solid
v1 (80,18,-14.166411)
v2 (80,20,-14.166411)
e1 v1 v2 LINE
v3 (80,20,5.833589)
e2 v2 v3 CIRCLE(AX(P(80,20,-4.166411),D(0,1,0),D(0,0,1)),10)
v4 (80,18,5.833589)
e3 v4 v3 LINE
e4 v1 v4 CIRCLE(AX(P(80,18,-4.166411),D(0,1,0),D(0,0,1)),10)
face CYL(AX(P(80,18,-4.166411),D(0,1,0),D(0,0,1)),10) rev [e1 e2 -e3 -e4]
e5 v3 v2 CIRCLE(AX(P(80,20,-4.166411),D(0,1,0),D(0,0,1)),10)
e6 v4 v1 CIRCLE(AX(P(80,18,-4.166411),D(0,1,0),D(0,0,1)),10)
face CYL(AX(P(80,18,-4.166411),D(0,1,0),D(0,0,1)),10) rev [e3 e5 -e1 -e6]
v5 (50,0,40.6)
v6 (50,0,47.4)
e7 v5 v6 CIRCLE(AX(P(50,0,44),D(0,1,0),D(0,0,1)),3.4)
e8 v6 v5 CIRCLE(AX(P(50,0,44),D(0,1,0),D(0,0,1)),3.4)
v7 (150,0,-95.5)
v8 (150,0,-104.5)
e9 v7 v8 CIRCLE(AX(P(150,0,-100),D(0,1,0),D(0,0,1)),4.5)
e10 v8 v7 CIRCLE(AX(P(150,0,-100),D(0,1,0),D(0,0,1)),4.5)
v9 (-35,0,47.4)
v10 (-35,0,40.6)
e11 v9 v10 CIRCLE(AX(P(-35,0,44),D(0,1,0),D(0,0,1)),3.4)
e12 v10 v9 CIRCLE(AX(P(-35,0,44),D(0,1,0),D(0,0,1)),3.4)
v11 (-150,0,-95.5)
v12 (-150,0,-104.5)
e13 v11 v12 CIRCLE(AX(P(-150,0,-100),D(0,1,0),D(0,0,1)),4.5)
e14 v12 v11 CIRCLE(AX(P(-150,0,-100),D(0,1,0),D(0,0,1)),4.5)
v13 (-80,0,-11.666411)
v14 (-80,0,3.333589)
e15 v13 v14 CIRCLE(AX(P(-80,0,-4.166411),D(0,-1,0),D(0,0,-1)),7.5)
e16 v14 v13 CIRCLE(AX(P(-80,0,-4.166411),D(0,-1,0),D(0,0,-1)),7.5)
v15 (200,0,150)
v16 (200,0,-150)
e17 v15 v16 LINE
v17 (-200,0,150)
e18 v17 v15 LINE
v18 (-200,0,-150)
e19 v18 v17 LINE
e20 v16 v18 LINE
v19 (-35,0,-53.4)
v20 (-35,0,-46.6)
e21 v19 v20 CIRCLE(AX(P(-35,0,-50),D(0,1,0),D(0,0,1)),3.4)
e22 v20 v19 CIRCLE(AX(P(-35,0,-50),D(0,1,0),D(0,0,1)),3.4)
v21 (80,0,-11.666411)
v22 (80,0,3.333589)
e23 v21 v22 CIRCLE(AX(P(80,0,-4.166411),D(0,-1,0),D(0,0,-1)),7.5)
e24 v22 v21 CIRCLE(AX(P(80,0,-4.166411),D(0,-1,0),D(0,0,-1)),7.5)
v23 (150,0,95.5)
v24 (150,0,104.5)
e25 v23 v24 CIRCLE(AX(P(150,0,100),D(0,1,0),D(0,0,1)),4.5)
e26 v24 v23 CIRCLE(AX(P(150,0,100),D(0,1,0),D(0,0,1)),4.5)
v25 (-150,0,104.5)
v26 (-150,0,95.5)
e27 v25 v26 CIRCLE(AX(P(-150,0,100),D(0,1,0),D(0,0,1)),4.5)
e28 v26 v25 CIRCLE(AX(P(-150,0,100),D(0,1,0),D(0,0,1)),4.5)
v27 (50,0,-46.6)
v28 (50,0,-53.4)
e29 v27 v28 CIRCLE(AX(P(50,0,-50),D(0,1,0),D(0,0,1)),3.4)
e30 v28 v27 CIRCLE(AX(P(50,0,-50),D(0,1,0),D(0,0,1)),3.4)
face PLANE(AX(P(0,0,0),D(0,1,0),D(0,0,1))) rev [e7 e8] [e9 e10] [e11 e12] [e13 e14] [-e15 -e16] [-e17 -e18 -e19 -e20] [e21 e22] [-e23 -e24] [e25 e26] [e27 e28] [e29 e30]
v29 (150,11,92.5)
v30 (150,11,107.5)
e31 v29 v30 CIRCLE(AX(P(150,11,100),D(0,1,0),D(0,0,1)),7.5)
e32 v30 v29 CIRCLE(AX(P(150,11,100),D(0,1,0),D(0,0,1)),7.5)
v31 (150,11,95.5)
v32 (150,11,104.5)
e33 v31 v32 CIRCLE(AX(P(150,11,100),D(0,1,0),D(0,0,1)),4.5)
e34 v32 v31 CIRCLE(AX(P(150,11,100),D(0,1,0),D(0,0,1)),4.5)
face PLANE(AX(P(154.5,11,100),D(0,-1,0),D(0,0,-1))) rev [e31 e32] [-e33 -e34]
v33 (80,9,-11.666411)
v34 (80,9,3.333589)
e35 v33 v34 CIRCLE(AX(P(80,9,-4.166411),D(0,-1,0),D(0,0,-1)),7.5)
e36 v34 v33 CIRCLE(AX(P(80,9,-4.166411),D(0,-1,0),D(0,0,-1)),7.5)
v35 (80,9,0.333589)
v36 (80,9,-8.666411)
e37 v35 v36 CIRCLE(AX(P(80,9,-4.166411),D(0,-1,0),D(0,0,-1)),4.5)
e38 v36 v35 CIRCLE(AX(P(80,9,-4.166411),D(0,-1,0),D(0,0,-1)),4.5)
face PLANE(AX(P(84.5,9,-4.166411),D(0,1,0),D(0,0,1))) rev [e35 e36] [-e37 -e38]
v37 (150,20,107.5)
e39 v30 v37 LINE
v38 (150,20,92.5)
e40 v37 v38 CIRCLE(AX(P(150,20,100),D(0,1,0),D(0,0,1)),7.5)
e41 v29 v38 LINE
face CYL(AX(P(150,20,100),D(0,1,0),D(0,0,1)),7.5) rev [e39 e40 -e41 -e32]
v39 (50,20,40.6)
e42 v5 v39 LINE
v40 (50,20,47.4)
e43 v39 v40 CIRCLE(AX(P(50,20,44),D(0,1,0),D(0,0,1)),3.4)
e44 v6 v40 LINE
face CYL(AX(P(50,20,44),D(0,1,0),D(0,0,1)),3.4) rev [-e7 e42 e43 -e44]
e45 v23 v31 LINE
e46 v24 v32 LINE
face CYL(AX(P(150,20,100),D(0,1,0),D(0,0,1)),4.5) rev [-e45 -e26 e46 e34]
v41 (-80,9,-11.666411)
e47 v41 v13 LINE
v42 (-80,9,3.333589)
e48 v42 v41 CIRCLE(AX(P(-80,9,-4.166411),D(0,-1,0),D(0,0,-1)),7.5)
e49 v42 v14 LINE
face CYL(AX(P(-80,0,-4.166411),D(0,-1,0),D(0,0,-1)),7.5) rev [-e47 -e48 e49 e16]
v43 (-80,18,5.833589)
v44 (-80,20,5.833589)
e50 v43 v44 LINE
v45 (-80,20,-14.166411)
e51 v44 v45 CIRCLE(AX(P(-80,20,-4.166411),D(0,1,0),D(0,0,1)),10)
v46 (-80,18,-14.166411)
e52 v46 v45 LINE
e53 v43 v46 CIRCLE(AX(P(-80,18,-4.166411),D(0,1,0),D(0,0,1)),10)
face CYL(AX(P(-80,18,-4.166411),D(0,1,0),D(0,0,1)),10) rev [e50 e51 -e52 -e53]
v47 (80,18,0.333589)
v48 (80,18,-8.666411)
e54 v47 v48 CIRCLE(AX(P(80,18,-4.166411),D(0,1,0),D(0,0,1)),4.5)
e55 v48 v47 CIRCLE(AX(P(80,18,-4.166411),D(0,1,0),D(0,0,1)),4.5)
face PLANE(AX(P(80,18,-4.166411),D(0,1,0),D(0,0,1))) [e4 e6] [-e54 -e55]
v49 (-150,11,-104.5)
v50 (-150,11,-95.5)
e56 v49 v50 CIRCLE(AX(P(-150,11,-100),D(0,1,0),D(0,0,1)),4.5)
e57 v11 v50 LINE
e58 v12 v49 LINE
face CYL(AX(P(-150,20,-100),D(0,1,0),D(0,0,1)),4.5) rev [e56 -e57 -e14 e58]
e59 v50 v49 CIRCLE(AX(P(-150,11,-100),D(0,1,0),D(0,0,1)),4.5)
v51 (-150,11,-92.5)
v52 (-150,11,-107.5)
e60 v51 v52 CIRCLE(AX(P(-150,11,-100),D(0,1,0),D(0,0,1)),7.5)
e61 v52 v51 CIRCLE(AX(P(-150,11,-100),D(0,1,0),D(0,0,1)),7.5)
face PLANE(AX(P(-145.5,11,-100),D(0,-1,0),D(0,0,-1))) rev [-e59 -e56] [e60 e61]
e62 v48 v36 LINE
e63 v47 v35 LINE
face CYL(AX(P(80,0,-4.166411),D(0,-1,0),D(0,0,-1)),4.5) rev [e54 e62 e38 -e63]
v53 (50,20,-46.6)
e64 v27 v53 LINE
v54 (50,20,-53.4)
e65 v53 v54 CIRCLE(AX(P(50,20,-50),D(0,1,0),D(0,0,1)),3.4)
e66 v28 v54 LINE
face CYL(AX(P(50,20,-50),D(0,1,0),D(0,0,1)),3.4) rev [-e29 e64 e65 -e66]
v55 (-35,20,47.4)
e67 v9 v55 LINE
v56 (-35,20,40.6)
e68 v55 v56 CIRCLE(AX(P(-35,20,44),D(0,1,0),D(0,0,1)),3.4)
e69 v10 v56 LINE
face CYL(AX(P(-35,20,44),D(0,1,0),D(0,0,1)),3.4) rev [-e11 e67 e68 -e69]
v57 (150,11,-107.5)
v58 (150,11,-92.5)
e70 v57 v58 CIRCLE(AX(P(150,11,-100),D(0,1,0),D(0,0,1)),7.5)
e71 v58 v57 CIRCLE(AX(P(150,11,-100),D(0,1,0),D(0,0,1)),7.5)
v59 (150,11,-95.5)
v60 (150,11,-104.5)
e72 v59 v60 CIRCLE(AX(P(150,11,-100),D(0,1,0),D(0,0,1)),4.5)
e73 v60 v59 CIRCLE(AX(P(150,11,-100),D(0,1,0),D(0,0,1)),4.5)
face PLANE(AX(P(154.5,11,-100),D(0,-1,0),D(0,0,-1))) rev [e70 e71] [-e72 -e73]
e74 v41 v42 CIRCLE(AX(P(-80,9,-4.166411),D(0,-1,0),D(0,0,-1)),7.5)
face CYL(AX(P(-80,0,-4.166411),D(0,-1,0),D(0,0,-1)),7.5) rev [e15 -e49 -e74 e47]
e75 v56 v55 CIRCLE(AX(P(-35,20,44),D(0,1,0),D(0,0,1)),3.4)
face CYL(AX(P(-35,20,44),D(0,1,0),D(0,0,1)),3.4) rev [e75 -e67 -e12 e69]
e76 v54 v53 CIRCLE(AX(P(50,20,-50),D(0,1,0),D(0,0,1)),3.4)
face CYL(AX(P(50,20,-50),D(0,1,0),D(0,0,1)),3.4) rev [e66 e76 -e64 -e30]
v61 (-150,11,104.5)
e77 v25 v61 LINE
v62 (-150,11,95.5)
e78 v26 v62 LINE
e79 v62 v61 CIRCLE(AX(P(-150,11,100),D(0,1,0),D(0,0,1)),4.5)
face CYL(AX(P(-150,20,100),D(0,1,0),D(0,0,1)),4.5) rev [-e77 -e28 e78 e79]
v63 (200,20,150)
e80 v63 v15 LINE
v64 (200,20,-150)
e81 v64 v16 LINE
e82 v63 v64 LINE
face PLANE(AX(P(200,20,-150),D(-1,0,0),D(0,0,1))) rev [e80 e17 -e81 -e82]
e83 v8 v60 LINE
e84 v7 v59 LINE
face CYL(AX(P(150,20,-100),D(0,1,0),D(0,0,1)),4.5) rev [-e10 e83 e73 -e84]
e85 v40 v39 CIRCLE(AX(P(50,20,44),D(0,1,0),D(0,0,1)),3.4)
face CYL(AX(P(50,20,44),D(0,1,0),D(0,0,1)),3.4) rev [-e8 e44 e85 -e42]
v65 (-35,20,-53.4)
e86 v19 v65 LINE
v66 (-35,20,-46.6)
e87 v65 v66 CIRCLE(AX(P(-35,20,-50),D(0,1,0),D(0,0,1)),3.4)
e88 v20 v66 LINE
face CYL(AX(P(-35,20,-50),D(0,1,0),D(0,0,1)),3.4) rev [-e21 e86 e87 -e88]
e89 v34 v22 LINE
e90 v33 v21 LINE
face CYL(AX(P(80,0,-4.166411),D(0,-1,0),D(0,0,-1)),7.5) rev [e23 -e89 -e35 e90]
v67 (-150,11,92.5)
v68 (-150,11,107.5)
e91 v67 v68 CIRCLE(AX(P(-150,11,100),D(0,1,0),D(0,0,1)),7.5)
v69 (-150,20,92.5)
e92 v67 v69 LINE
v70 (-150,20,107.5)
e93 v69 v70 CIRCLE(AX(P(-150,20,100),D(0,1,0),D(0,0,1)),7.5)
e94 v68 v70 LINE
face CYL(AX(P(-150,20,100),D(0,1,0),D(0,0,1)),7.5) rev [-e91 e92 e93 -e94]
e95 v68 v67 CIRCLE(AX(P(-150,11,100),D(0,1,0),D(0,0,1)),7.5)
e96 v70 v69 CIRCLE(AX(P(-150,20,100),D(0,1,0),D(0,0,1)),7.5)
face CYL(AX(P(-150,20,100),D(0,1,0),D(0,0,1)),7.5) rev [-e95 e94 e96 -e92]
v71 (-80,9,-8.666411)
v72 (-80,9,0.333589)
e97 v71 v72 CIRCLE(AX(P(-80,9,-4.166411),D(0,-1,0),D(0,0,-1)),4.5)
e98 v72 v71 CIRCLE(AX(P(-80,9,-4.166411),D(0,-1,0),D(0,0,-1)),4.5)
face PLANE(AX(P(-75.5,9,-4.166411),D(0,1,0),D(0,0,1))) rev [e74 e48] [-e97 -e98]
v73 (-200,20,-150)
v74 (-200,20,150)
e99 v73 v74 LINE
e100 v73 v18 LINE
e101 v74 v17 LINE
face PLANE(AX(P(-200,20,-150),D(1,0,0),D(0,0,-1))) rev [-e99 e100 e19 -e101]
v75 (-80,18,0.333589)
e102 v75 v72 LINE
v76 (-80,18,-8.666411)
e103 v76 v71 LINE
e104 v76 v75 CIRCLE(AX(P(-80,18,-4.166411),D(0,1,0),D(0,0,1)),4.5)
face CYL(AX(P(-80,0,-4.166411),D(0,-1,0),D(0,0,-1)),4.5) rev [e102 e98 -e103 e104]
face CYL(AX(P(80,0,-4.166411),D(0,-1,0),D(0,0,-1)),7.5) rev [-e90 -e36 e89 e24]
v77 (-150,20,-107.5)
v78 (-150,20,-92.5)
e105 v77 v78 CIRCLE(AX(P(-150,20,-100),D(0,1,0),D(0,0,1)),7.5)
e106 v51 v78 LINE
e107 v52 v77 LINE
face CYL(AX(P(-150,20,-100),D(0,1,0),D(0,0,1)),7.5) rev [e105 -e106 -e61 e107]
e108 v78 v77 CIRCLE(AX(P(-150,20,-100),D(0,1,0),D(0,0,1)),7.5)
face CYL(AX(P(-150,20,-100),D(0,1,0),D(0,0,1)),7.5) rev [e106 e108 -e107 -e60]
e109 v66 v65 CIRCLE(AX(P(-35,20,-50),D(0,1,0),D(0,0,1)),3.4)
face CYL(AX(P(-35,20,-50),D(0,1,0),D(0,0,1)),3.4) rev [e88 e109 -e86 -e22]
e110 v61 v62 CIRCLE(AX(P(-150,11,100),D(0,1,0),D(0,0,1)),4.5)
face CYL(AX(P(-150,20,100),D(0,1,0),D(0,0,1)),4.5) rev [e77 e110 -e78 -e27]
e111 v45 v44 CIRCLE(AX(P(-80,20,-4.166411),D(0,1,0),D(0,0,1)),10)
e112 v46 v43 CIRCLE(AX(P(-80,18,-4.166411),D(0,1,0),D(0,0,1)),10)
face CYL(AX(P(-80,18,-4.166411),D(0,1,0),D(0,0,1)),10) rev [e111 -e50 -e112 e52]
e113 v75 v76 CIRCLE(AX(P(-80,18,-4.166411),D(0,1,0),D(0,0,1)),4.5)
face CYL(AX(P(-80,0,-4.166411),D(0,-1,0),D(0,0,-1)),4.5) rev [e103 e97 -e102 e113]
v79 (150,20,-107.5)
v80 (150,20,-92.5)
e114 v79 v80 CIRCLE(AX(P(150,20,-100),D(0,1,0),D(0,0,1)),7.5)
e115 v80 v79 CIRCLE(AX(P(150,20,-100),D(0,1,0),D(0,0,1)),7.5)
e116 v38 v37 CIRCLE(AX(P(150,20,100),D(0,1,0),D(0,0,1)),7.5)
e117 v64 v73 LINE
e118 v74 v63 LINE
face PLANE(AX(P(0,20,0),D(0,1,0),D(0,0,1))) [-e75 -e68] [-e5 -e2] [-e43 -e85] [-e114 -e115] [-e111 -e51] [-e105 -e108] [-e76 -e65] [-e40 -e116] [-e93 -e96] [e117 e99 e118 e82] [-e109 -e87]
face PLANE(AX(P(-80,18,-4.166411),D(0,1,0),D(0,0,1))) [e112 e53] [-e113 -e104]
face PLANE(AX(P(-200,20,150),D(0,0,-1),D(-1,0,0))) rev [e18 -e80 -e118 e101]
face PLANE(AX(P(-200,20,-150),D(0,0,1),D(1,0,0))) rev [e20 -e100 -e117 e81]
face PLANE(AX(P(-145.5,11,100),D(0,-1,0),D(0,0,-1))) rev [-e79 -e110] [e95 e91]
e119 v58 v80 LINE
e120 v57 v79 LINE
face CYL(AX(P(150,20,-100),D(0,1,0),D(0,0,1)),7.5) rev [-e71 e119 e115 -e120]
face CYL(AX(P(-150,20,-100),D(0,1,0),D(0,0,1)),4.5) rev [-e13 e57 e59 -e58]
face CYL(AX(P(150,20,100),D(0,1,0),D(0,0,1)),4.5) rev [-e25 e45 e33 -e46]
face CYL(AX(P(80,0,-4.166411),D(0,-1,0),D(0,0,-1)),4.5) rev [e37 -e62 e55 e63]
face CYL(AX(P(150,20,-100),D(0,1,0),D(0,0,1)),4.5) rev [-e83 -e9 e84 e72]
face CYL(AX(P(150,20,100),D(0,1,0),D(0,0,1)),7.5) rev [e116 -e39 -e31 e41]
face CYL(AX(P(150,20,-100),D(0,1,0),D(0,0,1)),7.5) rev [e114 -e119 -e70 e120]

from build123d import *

# Parameters (mm, degrees)
SKETCH1_W                                            = 400
SKETCH1_H                                            = 300
BOSS_EXTRUDE1_DEPTH                                  = 20
HOLE_SIZE_PER_SOCKET_HEAD_CAP_SCREW_TYPE_D           = 9
HOLE_SIZE_PER_SOCKET_HEAD_CAP_SCREW_TYPE_CBORE_D     = 15
HOLE_SIZE_PER_SOCKET_HEAD_CAP_SCREW_TYPE_CBORE_DEPTH = 9
SKETCH5_R                                            = 10
CUT_EXTRUDE1_DEPTH                                   = 2
HOLE_SIZE_PER_SOCKET_HEAD_CAP_SCREW_2_D              = 9
HOLE_SIZE_PER_SOCKET_HEAD_CAP_SCREW_2_CBORE_D        = 15
HOLE_SIZE_PER_SOCKET_HEAD_CAP_SCREW_2_CBORE_DEPTH    = 9
M8_TAPPED_HOLE1_D                                    = 6.8


with BuildPart() as part:
    # Sketch1 → Boss-Extrude1 (new body)
    with BuildSketch(Plane(origin=(0, 0, 0), x_dir=(1, 0, 0), z_dir=(0, 1, 0))):
        Rectangle(SKETCH1_W, SKETCH1_H)
    extrude(amount=BOSS_EXTRUDE1_DEPTH)

    # Hole size per socket head cap screw type (through all)
    with Locations(Plane(origin=(0, 20, 0), x_dir=(1, 0, 0), z_dir=(0, 1, 0))):
        with Locations((-150, 100), (-150, -100), (150, 100), (150, -100)):
            CounterBoreHole(HOLE_SIZE_PER_SOCKET_HEAD_CAP_SCREW_TYPE_D / 2, HOLE_SIZE_PER_SOCKET_HEAD_CAP_SCREW_TYPE_CBORE_D / 2, HOLE_SIZE_PER_SOCKET_HEAD_CAP_SCREW_TYPE_CBORE_DEPTH)

    # Sketch5 → Cut-Extrude1 (cut)
    with BuildSketch(Plane(origin=(0, 20, 0), x_dir=(1, 0, 0), z_dir=(0, 1, 0))):
        with Locations(Location((-80, 4.166410727, 0), (0, 0, 270))):
            Circle(SKETCH5_R)
        with Locations(Location((80, 4.166410727, 0), (0, 0, 270))):
            Circle(SKETCH5_R)
    extrude(amount=-CUT_EXTRUDE1_DEPTH, mode=Mode.SUBTRACT)

    # Hole size per socket head cap screw  2 (through all)
    with Locations(Plane(origin=(0, 0, 0), x_dir=(-1, 0, 0), z_dir=(0, -1, 0))):
        with Locations((80, 4.166410727), (-80, 4.166410727)):
            CounterBoreHole(HOLE_SIZE_PER_SOCKET_HEAD_CAP_SCREW_2_D / 2, HOLE_SIZE_PER_SOCKET_HEAD_CAP_SCREW_2_CBORE_D / 2, HOLE_SIZE_PER_SOCKET_HEAD_CAP_SCREW_2_CBORE_DEPTH)

    # M8 Tapped Hole1 (through all)
    with Locations(Plane(origin=(0, 20, 0), x_dir=(1, 0, 0), z_dir=(0, 1, 0))):
        with Locations((-35, 50), (-35, -44), (50, -44), (50, 50)):
            Hole(M8_TAPPED_HOLE1_D / 2)


solid = part.part
